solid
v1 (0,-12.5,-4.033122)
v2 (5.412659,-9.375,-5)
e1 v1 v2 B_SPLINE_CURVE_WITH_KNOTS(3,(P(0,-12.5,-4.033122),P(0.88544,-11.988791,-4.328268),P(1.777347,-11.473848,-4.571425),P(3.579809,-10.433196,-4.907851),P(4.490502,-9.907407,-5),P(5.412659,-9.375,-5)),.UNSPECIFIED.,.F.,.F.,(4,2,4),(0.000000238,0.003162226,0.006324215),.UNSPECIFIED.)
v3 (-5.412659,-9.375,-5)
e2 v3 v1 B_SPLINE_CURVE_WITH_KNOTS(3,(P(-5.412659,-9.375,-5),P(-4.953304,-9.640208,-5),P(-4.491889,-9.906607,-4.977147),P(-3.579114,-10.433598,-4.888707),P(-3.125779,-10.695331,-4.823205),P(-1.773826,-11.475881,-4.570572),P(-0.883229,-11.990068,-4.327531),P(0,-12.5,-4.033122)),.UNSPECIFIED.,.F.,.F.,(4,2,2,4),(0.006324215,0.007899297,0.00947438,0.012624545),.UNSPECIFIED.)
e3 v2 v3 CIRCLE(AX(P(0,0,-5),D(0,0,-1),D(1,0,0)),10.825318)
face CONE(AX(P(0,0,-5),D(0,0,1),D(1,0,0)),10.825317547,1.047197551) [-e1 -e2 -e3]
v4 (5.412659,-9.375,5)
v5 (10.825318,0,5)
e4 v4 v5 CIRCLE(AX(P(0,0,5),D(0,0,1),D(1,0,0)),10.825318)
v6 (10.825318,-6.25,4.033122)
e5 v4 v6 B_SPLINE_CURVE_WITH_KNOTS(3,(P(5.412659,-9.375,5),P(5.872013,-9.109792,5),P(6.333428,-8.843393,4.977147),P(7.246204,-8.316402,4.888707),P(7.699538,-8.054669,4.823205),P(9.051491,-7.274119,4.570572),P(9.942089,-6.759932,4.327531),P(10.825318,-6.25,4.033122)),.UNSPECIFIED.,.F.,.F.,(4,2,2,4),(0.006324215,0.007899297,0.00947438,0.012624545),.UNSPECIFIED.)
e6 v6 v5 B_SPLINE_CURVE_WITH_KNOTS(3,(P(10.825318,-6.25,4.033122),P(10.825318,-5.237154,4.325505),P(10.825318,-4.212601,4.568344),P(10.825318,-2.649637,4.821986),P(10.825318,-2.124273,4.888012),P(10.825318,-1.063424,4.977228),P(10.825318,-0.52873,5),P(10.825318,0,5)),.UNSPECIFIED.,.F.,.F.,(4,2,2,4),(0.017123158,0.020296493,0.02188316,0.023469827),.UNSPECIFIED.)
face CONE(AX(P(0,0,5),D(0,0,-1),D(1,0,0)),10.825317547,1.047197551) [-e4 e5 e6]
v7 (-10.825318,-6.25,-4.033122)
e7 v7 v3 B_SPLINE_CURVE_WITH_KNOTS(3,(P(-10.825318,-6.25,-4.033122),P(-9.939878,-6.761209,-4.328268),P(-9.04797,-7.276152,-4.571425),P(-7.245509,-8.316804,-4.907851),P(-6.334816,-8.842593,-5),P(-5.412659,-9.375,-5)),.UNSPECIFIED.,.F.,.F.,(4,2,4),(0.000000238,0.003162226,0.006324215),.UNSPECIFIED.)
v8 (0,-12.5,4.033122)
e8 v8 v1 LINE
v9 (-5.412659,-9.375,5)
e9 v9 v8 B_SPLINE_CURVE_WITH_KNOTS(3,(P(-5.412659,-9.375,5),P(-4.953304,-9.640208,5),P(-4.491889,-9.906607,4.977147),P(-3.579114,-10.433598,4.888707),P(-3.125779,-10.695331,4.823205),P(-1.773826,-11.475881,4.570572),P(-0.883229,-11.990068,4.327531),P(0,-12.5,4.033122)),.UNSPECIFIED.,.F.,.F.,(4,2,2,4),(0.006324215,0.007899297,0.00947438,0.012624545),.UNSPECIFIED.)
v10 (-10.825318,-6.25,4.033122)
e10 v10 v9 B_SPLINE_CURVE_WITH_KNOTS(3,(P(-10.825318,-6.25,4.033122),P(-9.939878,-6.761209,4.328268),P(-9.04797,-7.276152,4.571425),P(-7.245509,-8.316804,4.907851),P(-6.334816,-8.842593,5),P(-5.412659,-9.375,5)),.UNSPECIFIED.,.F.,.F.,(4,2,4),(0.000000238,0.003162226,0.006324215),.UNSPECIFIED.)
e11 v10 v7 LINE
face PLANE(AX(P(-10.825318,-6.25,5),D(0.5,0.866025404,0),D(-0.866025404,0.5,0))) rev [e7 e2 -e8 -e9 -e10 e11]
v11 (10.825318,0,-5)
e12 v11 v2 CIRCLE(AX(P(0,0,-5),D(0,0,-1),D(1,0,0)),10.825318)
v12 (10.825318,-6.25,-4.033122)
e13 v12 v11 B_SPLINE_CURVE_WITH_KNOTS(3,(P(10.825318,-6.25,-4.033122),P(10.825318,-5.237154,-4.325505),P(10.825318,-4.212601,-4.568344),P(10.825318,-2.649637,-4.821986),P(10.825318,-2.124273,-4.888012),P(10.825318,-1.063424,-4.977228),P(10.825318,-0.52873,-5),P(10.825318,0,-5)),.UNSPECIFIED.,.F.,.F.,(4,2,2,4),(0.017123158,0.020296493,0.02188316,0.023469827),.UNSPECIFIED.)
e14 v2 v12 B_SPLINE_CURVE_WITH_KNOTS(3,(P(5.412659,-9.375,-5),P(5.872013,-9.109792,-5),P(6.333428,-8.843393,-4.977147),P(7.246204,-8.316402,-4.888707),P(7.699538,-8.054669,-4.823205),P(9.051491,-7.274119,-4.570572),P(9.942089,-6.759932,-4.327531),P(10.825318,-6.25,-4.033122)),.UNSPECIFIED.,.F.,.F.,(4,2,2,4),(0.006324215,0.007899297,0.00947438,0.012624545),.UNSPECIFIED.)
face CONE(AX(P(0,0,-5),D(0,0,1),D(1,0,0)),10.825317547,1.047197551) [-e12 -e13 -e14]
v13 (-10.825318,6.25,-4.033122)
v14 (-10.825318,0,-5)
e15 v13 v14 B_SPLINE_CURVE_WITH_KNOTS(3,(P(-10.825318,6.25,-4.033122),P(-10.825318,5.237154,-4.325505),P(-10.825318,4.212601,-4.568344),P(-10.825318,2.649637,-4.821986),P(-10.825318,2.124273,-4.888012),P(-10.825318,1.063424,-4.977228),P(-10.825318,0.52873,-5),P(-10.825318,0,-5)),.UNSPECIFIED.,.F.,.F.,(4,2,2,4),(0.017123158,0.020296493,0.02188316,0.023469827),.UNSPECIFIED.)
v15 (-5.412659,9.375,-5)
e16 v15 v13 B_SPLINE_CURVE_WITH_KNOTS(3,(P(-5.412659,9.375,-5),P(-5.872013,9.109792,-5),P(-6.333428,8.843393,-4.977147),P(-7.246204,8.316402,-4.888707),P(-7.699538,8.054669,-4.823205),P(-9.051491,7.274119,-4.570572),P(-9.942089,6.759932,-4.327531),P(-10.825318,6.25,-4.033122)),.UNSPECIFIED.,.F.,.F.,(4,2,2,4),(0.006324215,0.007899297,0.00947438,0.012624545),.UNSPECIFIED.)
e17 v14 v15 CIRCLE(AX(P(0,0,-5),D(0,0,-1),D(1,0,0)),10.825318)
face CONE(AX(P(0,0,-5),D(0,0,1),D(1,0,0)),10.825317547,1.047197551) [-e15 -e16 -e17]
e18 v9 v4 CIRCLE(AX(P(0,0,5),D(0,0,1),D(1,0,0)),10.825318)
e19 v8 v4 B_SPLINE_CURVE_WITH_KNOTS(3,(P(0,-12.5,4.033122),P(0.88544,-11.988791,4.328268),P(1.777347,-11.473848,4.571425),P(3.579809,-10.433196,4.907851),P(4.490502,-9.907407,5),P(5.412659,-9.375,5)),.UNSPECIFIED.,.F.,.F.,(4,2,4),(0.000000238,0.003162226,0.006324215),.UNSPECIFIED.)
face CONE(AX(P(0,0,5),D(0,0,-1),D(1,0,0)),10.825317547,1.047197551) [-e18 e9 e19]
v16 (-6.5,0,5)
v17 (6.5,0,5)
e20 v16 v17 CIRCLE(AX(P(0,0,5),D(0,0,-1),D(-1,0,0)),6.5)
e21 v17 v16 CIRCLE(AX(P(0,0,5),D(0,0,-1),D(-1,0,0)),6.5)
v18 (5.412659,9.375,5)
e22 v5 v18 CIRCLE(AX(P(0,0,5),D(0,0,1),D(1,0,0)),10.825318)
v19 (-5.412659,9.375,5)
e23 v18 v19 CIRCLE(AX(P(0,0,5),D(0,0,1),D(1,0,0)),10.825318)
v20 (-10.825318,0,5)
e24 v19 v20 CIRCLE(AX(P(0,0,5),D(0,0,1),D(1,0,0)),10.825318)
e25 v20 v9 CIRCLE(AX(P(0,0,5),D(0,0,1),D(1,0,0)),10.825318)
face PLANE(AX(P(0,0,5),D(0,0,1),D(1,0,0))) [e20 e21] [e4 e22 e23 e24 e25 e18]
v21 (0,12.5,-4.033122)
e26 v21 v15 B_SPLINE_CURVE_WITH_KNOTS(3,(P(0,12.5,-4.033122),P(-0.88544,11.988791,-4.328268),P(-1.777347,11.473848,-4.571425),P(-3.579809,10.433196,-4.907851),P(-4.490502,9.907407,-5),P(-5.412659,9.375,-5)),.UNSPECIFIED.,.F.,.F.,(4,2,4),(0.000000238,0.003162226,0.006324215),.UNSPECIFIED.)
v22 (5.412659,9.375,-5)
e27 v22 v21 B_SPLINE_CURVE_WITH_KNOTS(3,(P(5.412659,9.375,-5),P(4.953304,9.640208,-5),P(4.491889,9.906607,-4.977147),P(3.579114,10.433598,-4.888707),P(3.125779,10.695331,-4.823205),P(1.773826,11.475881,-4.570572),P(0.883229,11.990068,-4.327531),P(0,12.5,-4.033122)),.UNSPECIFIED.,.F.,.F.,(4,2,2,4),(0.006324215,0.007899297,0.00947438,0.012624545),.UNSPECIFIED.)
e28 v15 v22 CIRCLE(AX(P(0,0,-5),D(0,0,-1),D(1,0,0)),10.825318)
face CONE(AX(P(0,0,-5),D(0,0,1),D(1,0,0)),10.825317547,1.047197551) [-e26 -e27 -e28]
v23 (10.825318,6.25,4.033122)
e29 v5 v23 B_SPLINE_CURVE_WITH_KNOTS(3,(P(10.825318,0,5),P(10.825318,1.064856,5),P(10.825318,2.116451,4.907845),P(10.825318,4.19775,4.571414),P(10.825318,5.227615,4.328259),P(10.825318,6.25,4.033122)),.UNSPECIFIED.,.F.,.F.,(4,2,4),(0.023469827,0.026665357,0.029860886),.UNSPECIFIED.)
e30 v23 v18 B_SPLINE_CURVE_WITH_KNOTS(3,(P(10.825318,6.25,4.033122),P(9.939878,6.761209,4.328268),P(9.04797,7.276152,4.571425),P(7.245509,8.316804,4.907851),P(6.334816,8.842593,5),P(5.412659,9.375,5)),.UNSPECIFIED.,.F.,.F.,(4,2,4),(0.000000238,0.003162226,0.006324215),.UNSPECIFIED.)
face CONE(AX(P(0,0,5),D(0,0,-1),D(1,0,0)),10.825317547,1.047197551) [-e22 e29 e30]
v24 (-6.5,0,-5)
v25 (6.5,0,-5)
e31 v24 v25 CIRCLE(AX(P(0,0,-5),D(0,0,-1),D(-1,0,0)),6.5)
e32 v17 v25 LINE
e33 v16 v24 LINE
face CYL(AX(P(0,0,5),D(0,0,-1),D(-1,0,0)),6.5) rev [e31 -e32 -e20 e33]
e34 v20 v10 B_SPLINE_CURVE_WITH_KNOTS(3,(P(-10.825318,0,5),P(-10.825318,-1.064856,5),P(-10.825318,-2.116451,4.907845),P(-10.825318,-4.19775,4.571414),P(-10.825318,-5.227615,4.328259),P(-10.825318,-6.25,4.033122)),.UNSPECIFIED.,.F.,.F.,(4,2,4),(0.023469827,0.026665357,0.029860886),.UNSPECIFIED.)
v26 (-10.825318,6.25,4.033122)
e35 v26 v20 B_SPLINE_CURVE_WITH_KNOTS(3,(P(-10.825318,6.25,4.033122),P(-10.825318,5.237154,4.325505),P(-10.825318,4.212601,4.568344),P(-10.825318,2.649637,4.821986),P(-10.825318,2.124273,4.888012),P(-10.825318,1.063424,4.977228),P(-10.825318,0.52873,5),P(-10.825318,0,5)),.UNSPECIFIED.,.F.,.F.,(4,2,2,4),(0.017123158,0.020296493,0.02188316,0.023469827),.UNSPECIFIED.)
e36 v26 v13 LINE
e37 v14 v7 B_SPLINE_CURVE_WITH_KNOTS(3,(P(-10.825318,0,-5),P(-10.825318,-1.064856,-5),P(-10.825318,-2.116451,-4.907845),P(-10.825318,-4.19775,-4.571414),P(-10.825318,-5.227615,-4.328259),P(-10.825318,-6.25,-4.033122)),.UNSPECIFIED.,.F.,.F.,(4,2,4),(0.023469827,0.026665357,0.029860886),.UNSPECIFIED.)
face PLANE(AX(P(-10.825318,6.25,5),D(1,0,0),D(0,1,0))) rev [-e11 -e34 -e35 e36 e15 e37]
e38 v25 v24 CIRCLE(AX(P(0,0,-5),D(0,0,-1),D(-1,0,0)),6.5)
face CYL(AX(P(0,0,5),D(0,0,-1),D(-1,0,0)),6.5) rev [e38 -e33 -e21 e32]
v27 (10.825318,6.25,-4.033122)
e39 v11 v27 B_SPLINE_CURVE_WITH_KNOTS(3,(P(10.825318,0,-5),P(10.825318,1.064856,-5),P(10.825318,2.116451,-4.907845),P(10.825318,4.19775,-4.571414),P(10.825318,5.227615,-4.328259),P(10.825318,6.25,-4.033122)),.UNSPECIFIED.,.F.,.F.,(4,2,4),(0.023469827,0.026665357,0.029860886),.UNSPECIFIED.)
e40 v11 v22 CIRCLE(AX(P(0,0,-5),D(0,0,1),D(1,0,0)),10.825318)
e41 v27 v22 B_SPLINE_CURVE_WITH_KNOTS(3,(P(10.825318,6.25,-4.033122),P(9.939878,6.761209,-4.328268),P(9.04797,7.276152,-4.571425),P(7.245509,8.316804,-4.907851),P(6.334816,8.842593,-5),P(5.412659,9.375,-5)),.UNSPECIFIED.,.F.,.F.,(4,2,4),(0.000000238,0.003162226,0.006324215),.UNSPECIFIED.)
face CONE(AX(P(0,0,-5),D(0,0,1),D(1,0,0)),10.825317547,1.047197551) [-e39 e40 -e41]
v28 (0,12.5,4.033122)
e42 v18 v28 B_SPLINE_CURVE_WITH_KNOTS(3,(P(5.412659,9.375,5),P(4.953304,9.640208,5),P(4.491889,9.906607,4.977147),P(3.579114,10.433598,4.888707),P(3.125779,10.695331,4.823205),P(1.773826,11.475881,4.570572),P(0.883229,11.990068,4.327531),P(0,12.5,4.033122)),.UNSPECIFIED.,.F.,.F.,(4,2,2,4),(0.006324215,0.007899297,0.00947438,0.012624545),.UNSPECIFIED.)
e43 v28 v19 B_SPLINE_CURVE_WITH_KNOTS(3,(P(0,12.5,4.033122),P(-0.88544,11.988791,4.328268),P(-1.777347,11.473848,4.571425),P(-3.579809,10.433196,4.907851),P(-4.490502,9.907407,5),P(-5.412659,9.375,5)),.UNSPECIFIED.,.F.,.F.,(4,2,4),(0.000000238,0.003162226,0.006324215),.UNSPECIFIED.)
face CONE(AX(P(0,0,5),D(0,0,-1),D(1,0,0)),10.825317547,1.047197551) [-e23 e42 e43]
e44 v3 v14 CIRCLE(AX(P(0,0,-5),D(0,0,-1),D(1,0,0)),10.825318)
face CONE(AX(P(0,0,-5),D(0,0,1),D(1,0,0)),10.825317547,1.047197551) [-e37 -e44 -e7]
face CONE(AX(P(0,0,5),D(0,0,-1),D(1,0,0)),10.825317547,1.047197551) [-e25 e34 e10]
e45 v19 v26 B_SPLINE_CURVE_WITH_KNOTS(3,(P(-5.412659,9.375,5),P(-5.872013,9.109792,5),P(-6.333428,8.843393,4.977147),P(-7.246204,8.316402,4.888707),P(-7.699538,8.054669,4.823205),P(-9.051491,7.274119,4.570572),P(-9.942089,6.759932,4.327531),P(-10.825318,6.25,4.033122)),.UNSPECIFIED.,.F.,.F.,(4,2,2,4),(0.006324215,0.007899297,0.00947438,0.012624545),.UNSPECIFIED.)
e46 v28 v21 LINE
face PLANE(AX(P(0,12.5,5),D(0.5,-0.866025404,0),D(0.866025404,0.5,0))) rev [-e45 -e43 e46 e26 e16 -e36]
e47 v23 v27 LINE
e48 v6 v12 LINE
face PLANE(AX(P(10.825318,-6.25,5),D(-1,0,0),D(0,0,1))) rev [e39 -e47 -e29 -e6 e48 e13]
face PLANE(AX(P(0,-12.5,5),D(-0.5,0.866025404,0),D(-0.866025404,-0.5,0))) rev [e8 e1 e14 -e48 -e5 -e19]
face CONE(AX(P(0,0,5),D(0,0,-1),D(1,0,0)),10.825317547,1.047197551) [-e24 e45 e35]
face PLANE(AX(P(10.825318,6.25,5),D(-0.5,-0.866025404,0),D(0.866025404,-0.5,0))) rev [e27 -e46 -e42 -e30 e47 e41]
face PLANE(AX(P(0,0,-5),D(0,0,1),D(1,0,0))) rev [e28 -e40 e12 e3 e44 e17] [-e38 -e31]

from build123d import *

# Parameters (mm, degrees)
BOSS_EXTRUDE1_DEPTH     = 5
SKETCH2_OUTSIDE_W       = 65.202
SKETCH2_OUTSIDE_H       = 68.552
SKETCH2_OUTSIDE_R       = 10.825317547
CUT_EXTRUDE1_DEPTH      = 10
CUT_EXTRUDE1_DRAFT      = -60
MIRROR1_COPY_1_SKETCH_W = 65.202
MIRROR1_COPY_1_SKETCH_H = 68.552
MIRROR1_COPY_1_SKETCH_R = 10.825317547
MIRROR1_COPY_1_DEPTH    = 10
MIRROR1_COPY_1_DRAFT    = -60
SKETCH3_R               = 6.5
CUT_EXTRUDE2_DEPTH      = 10


with BuildPart() as part:
    # Sketch1 → Boss-Extrude1 (new, symmetric)
    with BuildSketch(Plane.XY):
        Polygon((0, 12.5), (-10.825317547, 6.25), (-10.825317547, -6.25), (0, -12.5), (10.825317547, -6.25), (10.825317547, 6.25), align=None)
    extrude(amount=BOSS_EXTRUDE1_DEPTH, both=True)


with BuildPart() as cut_extrude1_tool:
    # Sketch2 outside → Cut-Extrude1 (with draft: the straight prism first)
    with BuildSketch(Plane.XY.offset(5)):
        Rectangle(SKETCH2_OUTSIDE_W, SKETCH2_OUTSIDE_H)
        Circle(SKETCH2_OUTSIDE_R, mode=Mode.SUBTRACT)
    extrude(amount=-CUT_EXTRUDE1_DEPTH)
    # Cut-Extrude1: the draft: its side faces are tilted about the plane it starts from
    cut_extrude1_sides = [cut_extrude1_tool.faces().sort_by_distance(p)[0] for p in [
        (0, -34.276, 0),
        (32.601, 0, 0),
        (0, 34.276, 0),
        (-32.601, 0, 0),
        (-10.825317547, 0, 0),
    ]]
    draft(cut_extrude1_sides, Plane.XY.offset(5), CUT_EXTRUDE1_DRAFT)


with BuildPart() as part_1:
    add(part.part)

    # Cut-Extrude1: cut by cut_extrude1_tool
    add(cut_extrude1_tool.part, mode=Mode.SUBTRACT)


with BuildPart() as mirror1_copy_1_tool:
    # Mirror1 copy 1 sketch → Mirror1 copy 1 (with draft: the straight prism first)
    with BuildSketch(Plane(origin=(0, 0, -5), x_dir=(1, 0, 0), z_dir=(0, 0, -1))):
        Rectangle(MIRROR1_COPY_1_SKETCH_W, MIRROR1_COPY_1_SKETCH_H)
        Circle(MIRROR1_COPY_1_SKETCH_R, mode=Mode.SUBTRACT)
    extrude(amount=-MIRROR1_COPY_1_DEPTH)
    # Mirror1 copy 1: the draft: its side faces are tilted about the plane it starts from
    mirror1_copy_1_sides = [mirror1_copy_1_tool.faces().sort_by_distance(p)[0] for p in [
        (0, -34.276, 0),
        (32.601, 0, 0),
        (0, 34.276, 0),
        (-32.601, 0, 0),
        (-10.825317547, 0, 0),
    ]]
    draft(mirror1_copy_1_sides, Plane(origin=(0, 0, -5), x_dir=(1, 0, 0), z_dir=(0, 0, -1)), MIRROR1_COPY_1_DRAFT)


with BuildPart() as part_2:
    add(part_1.part)

    # Mirror1 copy 1: cut by mirror1_copy_1_tool
    add(mirror1_copy_1_tool.part, mode=Mode.SUBTRACT)

    # Sketch3 → Cut-Extrude2 (cut)
    with BuildSketch(Plane(origin=(0, 0, -5), x_dir=(-1, 0, 0), z_dir=(0, 0, -1))):
        Circle(SKETCH3_R)
    extrude(amount=-CUT_EXTRUDE2_DEPTH, mode=Mode.SUBTRACT)


solid = part_2.part
